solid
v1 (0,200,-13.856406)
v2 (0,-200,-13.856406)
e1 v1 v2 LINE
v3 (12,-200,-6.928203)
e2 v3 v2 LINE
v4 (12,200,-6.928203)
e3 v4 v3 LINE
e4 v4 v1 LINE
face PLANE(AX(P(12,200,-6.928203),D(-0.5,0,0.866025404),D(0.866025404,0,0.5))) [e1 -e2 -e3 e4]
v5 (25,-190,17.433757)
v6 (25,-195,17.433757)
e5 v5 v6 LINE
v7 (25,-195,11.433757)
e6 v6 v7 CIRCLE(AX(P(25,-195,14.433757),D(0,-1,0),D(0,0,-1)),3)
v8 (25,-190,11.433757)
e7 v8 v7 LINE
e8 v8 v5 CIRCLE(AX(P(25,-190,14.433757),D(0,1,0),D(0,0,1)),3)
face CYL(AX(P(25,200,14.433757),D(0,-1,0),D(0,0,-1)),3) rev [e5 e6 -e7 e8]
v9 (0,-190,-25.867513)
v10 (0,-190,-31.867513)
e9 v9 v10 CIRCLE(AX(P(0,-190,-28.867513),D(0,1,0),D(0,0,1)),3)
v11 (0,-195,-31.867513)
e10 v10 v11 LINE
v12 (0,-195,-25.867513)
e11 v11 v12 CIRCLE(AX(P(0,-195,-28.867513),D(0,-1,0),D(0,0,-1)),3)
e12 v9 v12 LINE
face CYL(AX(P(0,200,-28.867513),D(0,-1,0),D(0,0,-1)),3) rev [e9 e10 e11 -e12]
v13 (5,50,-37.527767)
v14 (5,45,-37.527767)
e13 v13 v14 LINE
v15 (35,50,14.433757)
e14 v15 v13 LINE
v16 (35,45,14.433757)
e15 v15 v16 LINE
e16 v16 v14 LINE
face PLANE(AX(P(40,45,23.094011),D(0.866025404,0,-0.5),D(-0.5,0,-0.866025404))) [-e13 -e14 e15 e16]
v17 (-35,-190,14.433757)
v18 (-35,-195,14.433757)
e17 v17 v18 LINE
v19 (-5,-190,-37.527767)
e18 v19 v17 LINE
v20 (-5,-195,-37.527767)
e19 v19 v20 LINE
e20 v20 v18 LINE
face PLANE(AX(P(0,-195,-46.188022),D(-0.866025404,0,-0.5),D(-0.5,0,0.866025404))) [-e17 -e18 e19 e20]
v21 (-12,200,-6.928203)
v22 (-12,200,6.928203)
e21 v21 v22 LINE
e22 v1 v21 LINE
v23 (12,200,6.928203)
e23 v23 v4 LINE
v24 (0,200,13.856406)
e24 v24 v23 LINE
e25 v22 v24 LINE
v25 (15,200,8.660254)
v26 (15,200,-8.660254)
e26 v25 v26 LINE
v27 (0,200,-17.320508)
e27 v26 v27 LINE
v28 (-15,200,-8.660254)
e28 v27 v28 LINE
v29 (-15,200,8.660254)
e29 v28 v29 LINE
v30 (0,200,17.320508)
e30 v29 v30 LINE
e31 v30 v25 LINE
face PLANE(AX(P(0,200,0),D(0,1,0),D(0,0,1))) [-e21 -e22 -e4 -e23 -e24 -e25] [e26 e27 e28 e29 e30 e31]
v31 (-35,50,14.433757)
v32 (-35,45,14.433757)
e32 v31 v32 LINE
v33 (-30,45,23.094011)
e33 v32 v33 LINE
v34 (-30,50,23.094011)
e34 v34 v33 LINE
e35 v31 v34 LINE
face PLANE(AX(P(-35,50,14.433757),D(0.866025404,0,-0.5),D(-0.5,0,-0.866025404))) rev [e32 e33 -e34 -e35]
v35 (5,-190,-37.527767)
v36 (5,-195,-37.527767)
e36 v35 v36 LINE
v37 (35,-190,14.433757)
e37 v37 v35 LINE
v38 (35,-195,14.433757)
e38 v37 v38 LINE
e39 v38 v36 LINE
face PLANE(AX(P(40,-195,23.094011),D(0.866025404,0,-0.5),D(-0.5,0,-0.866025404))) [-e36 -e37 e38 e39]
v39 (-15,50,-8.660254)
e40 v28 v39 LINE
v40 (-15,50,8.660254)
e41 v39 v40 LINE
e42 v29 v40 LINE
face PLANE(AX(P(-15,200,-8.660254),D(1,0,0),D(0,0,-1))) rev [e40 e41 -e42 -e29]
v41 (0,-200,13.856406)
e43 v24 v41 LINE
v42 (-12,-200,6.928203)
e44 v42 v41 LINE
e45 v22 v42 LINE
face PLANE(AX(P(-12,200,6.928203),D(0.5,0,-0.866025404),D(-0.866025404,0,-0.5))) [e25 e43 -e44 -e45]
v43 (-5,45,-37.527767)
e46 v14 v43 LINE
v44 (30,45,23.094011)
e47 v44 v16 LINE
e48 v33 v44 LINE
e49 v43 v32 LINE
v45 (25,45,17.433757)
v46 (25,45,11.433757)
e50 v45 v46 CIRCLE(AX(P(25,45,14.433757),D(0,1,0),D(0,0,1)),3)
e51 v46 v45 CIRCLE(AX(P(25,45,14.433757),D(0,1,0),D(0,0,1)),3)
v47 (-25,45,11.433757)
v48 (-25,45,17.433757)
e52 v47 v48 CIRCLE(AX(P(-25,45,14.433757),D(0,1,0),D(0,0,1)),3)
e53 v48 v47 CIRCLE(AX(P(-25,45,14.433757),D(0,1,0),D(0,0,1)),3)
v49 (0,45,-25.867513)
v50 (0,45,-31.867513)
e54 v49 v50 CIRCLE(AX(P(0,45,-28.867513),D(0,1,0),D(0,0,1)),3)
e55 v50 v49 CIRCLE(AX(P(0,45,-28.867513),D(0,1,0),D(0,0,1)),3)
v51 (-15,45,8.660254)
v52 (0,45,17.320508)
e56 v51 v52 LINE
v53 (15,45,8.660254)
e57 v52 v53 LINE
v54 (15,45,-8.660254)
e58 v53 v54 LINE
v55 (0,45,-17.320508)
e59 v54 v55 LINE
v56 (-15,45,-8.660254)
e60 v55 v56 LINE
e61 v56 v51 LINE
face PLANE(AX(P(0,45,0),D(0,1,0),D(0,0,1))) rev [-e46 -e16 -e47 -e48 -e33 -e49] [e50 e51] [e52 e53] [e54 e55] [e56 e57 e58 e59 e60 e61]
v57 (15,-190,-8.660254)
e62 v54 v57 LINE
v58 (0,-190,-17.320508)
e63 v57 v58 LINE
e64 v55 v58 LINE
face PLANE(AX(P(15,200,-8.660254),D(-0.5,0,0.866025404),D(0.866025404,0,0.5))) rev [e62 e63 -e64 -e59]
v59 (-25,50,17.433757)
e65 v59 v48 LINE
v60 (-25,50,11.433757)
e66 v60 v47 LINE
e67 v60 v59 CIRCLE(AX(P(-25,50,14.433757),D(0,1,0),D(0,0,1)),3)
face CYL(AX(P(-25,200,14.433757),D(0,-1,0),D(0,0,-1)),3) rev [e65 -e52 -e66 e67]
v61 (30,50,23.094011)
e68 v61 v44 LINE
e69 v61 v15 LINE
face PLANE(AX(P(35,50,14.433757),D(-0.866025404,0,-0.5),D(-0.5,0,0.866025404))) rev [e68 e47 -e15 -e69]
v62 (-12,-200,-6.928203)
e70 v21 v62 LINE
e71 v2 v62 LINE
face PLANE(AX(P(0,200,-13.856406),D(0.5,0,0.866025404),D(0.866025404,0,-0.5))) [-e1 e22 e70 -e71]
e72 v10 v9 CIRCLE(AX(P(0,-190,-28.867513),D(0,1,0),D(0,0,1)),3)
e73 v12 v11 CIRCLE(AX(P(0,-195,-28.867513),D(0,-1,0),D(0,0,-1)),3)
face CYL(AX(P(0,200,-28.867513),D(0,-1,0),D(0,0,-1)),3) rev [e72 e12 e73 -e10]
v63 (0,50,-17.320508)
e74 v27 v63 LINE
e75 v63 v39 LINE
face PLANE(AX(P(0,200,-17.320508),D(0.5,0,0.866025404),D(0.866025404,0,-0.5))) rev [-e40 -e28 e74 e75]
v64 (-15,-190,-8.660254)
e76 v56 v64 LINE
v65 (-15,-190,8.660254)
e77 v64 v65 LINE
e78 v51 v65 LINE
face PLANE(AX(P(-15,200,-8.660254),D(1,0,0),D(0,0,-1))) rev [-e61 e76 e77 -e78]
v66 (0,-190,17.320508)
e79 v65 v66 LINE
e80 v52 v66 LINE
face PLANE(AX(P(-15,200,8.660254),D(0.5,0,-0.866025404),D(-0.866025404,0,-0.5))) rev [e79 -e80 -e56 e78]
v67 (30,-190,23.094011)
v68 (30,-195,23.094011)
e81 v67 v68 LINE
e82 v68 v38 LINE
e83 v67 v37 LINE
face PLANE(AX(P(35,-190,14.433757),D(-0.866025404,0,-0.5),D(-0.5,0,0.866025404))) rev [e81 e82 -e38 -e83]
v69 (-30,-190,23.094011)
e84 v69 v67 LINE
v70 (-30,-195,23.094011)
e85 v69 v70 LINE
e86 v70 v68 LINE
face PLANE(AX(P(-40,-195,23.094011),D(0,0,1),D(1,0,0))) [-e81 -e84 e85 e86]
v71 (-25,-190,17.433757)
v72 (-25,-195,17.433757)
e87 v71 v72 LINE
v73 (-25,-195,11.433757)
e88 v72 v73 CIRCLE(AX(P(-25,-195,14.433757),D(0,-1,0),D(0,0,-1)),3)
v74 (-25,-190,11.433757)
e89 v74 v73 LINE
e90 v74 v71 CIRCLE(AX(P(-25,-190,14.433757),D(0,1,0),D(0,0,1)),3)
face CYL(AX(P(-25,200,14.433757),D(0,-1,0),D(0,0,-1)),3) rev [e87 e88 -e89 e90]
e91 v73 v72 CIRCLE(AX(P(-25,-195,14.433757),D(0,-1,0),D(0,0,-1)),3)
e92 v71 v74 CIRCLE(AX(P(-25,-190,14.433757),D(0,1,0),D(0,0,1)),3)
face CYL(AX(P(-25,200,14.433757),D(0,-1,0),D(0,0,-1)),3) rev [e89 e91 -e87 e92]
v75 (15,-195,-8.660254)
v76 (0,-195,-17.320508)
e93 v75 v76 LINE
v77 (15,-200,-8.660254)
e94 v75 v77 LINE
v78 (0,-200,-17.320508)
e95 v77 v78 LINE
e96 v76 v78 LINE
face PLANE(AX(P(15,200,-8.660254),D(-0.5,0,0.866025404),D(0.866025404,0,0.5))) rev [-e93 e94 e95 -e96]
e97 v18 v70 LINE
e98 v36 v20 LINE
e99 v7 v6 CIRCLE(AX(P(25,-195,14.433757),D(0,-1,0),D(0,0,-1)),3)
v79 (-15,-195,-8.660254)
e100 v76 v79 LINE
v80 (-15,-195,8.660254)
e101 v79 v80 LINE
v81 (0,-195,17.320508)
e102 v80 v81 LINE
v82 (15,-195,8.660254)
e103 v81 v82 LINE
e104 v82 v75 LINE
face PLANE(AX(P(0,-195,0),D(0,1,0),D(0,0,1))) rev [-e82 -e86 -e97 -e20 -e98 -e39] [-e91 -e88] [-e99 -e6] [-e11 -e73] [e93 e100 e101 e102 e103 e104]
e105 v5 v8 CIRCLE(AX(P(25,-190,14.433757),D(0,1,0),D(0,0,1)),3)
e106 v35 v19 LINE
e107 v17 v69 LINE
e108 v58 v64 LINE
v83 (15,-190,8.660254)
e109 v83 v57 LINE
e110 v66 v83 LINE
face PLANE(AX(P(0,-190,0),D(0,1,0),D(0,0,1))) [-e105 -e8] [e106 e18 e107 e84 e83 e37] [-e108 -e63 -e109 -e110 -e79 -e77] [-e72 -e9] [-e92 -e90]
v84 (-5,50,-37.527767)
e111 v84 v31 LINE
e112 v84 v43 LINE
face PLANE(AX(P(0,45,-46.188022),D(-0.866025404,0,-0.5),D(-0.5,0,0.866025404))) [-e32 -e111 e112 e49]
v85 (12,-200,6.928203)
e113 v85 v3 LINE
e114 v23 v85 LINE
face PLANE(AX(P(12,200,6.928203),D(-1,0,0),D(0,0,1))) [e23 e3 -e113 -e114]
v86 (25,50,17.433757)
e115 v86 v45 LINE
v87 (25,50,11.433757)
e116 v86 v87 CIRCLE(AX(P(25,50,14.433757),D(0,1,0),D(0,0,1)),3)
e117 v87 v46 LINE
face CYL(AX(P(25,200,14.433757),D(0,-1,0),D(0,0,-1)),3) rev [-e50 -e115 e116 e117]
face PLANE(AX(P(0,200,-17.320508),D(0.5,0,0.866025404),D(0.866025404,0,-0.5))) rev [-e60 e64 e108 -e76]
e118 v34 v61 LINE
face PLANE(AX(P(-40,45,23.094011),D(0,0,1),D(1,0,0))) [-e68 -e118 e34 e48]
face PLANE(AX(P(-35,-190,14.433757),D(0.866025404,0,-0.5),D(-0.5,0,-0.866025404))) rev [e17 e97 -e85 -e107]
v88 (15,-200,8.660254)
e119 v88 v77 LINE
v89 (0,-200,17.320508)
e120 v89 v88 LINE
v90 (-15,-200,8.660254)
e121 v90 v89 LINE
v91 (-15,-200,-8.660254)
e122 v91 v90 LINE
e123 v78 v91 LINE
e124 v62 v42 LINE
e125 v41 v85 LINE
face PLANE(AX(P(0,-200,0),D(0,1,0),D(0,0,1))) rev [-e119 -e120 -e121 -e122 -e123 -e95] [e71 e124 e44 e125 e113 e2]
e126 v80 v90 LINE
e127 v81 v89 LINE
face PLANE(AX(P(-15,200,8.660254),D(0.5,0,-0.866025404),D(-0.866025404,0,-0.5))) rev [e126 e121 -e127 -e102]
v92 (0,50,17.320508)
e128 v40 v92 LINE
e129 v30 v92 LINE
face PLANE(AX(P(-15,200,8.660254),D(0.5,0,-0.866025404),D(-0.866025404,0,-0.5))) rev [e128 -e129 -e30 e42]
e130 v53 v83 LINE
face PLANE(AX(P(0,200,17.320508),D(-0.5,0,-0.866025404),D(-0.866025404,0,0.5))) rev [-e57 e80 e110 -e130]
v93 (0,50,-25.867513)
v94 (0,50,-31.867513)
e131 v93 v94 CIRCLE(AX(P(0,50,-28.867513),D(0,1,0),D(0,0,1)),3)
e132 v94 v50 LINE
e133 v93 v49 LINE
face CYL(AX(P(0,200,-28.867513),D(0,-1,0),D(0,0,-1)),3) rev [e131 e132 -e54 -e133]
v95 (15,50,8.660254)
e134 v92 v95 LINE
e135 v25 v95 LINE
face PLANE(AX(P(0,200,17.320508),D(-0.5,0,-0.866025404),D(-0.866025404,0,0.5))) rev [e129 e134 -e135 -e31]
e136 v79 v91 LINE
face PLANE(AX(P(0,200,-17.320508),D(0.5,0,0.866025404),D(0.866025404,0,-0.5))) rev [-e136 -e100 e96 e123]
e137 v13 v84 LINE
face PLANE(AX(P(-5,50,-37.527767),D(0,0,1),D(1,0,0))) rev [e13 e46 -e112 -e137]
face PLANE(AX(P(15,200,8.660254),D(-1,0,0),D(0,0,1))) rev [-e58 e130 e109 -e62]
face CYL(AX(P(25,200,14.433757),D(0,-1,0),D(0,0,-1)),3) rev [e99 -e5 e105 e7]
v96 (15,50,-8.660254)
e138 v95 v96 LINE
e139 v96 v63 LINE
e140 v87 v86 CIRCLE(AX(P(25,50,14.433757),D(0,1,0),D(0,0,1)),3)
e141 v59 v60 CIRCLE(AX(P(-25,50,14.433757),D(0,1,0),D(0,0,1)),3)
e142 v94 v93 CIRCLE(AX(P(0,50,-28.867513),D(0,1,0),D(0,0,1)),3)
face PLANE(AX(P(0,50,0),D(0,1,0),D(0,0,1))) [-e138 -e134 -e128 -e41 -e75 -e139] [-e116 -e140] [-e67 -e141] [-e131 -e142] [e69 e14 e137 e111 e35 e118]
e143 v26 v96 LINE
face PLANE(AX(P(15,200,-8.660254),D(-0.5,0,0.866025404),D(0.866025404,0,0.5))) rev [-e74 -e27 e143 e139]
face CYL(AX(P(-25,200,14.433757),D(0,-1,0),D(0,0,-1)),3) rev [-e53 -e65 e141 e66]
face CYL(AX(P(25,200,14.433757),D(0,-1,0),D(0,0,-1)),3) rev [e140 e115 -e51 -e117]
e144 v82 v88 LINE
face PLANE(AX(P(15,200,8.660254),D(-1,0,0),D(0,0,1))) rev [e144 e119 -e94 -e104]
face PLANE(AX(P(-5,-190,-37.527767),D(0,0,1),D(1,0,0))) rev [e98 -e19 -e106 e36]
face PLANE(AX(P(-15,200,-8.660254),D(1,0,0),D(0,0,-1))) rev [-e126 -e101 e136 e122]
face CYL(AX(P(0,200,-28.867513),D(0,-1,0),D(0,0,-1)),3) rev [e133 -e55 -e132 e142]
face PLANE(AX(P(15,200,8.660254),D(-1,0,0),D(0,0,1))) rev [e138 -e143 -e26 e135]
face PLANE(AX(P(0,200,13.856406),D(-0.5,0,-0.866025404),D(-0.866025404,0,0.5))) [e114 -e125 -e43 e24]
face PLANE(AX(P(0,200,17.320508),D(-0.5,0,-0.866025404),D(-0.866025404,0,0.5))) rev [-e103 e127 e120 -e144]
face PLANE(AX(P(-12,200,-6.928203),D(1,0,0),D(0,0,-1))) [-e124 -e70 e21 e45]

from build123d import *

# Parameters (mm, degrees)
BOSS_EXTRUDE1_DEPTH = 200
BOSS_EXTRUDE2_DEPTH = 5
CUT_EXTRUDE1_DEPTH  = 5
LPATTERN1_COUNT     = 4
LPATTERN1_PITCH     = 120
SKETCH5_R           = 3
CUT_EXTRUDE2_DEPTH  = 399.319386088
CUT_EXTRUDE4_DEPTH  = 10
CUT_EXTRUDE5_DEPTH  = 10


with BuildPart() as part:
    # Sketch1 → Boss-Extrude1 (new, symmetric)
    with BuildSketch(Plane(origin=(0, 0, 0), x_dir=(1, 0, 0), z_dir=(0, 1, 0))):
        Polygon((0, 17.320508076), (-15, 8.660254038), (-15, -8.660254038), (0, -17.320508076), (15, -8.660254038), (15, 8.660254038), align=None)
        Polygon((-12, 6.92820323), (-12, -6.92820323), (0, -13.856406461), (12, -6.92820323), (12, 6.92820323), (0, 13.856406461), align=None, mode=Mode.SUBTRACT)
    extrude(amount=BOSS_EXTRUDE1_DEPTH, both=True)

    # Sketch2 → Boss-Extrude2 (add)
    with BuildSketch(Plane(origin=(0, 170, 0), x_dir=(1, 0, 0), z_dir=(0, 1, 0))):
        Polygon((0, 46.188021535), (-40, -23.094010768), (40, -23.094010768), align=None)
        Polygon((15, 8.660254038), (0, 17.320508076), (-15, 8.660254038), (-15, -8.660254038), (0, -17.320508076), (15, -8.660254038), align=None, mode=Mode.SUBTRACT)
    boss_extrude2 = extrude(amount=-BOSS_EXTRUDE2_DEPTH)

    # Sketch3 → Cut-Extrude1 (cut)
    with BuildSketch(Plane.XZ.offset(-165)):
        Polygon((0, -46.188021535), (5, -37.527767497), (-5, -37.527767497), align=None)
        Polygon((40, 23.094010768), (30, 23.094010768), (35, 14.43375673), align=None)
        Polygon((-40, 23.094010768), (-35, 14.43375673), (-30, 23.094010768), align=None)
    cut_extrude1 = extrude(amount=-CUT_EXTRUDE1_DEPTH, mode=Mode.SUBTRACT)

    # LPattern1: Boss-Extrude2, Cut-Extrude1 ×4
    with Locations(*[(0, -i * LPATTERN1_PITCH, 0) for i in range(1, LPATTERN1_COUNT)]):
        add(boss_extrude2)
        add(cut_extrude1, mode=Mode.SUBTRACT)

    # Sketch5 → Cut-Extrude2 (cut, through all)
    with BuildSketch(Plane.XZ.offset(195)):
        with Locations(Location((-25, 14.43375673, 0), (0, 0, 270))):
            Circle(SKETCH5_R)
        with Locations(Location((25, 14.43375673, 0), (0, 0, 270))):
            Circle(SKETCH5_R)
        with Locations(Location((0, -28.867513459, 0), (0, 0, 270))):
            Circle(SKETCH5_R)
    extrude(amount=-CUT_EXTRUDE2_DEPTH, mode=Mode.SUBTRACT)

    # Sketch7 → Cut-Extrude4 (cut)
    with BuildSketch(Plane.XZ.offset(-165)):
        Polygon((30, 23.094010768), (-30, 23.094010768), (-35, 14.43375673), (-5, -37.527767497), (5, -37.527767497), (35, 14.43375673), align=None)
        Polygon((-15, -8.660254038), (-15, 8.660254038), (0, 17.320508076), (15, 8.660254038), (15, -8.660254038), (0, -17.320508076), align=None, mode=Mode.SUBTRACT)
    extrude(amount=-CUT_EXTRUDE4_DEPTH, mode=Mode.SUBTRACT)

    # Sketch8 → Cut-Extrude5 (cut)
    with BuildSketch(Plane.XZ.offset(75)):
        Polygon((-35, 14.43375673), (-5, -37.527767497), (5, -37.527767497), (35, 14.43375673), (30, 23.094010768), (-30, 23.094010768), align=None)
        Polygon((0, 17.320508076), (15, 8.660254038), (15, -8.660254038), (0, -17.320508076), (-15, -8.660254038), (-15, 8.660254038), align=None, mode=Mode.SUBTRACT)
    extrude(amount=-CUT_EXTRUDE5_DEPTH, mode=Mode.SUBTRACT)


solid = part.part
